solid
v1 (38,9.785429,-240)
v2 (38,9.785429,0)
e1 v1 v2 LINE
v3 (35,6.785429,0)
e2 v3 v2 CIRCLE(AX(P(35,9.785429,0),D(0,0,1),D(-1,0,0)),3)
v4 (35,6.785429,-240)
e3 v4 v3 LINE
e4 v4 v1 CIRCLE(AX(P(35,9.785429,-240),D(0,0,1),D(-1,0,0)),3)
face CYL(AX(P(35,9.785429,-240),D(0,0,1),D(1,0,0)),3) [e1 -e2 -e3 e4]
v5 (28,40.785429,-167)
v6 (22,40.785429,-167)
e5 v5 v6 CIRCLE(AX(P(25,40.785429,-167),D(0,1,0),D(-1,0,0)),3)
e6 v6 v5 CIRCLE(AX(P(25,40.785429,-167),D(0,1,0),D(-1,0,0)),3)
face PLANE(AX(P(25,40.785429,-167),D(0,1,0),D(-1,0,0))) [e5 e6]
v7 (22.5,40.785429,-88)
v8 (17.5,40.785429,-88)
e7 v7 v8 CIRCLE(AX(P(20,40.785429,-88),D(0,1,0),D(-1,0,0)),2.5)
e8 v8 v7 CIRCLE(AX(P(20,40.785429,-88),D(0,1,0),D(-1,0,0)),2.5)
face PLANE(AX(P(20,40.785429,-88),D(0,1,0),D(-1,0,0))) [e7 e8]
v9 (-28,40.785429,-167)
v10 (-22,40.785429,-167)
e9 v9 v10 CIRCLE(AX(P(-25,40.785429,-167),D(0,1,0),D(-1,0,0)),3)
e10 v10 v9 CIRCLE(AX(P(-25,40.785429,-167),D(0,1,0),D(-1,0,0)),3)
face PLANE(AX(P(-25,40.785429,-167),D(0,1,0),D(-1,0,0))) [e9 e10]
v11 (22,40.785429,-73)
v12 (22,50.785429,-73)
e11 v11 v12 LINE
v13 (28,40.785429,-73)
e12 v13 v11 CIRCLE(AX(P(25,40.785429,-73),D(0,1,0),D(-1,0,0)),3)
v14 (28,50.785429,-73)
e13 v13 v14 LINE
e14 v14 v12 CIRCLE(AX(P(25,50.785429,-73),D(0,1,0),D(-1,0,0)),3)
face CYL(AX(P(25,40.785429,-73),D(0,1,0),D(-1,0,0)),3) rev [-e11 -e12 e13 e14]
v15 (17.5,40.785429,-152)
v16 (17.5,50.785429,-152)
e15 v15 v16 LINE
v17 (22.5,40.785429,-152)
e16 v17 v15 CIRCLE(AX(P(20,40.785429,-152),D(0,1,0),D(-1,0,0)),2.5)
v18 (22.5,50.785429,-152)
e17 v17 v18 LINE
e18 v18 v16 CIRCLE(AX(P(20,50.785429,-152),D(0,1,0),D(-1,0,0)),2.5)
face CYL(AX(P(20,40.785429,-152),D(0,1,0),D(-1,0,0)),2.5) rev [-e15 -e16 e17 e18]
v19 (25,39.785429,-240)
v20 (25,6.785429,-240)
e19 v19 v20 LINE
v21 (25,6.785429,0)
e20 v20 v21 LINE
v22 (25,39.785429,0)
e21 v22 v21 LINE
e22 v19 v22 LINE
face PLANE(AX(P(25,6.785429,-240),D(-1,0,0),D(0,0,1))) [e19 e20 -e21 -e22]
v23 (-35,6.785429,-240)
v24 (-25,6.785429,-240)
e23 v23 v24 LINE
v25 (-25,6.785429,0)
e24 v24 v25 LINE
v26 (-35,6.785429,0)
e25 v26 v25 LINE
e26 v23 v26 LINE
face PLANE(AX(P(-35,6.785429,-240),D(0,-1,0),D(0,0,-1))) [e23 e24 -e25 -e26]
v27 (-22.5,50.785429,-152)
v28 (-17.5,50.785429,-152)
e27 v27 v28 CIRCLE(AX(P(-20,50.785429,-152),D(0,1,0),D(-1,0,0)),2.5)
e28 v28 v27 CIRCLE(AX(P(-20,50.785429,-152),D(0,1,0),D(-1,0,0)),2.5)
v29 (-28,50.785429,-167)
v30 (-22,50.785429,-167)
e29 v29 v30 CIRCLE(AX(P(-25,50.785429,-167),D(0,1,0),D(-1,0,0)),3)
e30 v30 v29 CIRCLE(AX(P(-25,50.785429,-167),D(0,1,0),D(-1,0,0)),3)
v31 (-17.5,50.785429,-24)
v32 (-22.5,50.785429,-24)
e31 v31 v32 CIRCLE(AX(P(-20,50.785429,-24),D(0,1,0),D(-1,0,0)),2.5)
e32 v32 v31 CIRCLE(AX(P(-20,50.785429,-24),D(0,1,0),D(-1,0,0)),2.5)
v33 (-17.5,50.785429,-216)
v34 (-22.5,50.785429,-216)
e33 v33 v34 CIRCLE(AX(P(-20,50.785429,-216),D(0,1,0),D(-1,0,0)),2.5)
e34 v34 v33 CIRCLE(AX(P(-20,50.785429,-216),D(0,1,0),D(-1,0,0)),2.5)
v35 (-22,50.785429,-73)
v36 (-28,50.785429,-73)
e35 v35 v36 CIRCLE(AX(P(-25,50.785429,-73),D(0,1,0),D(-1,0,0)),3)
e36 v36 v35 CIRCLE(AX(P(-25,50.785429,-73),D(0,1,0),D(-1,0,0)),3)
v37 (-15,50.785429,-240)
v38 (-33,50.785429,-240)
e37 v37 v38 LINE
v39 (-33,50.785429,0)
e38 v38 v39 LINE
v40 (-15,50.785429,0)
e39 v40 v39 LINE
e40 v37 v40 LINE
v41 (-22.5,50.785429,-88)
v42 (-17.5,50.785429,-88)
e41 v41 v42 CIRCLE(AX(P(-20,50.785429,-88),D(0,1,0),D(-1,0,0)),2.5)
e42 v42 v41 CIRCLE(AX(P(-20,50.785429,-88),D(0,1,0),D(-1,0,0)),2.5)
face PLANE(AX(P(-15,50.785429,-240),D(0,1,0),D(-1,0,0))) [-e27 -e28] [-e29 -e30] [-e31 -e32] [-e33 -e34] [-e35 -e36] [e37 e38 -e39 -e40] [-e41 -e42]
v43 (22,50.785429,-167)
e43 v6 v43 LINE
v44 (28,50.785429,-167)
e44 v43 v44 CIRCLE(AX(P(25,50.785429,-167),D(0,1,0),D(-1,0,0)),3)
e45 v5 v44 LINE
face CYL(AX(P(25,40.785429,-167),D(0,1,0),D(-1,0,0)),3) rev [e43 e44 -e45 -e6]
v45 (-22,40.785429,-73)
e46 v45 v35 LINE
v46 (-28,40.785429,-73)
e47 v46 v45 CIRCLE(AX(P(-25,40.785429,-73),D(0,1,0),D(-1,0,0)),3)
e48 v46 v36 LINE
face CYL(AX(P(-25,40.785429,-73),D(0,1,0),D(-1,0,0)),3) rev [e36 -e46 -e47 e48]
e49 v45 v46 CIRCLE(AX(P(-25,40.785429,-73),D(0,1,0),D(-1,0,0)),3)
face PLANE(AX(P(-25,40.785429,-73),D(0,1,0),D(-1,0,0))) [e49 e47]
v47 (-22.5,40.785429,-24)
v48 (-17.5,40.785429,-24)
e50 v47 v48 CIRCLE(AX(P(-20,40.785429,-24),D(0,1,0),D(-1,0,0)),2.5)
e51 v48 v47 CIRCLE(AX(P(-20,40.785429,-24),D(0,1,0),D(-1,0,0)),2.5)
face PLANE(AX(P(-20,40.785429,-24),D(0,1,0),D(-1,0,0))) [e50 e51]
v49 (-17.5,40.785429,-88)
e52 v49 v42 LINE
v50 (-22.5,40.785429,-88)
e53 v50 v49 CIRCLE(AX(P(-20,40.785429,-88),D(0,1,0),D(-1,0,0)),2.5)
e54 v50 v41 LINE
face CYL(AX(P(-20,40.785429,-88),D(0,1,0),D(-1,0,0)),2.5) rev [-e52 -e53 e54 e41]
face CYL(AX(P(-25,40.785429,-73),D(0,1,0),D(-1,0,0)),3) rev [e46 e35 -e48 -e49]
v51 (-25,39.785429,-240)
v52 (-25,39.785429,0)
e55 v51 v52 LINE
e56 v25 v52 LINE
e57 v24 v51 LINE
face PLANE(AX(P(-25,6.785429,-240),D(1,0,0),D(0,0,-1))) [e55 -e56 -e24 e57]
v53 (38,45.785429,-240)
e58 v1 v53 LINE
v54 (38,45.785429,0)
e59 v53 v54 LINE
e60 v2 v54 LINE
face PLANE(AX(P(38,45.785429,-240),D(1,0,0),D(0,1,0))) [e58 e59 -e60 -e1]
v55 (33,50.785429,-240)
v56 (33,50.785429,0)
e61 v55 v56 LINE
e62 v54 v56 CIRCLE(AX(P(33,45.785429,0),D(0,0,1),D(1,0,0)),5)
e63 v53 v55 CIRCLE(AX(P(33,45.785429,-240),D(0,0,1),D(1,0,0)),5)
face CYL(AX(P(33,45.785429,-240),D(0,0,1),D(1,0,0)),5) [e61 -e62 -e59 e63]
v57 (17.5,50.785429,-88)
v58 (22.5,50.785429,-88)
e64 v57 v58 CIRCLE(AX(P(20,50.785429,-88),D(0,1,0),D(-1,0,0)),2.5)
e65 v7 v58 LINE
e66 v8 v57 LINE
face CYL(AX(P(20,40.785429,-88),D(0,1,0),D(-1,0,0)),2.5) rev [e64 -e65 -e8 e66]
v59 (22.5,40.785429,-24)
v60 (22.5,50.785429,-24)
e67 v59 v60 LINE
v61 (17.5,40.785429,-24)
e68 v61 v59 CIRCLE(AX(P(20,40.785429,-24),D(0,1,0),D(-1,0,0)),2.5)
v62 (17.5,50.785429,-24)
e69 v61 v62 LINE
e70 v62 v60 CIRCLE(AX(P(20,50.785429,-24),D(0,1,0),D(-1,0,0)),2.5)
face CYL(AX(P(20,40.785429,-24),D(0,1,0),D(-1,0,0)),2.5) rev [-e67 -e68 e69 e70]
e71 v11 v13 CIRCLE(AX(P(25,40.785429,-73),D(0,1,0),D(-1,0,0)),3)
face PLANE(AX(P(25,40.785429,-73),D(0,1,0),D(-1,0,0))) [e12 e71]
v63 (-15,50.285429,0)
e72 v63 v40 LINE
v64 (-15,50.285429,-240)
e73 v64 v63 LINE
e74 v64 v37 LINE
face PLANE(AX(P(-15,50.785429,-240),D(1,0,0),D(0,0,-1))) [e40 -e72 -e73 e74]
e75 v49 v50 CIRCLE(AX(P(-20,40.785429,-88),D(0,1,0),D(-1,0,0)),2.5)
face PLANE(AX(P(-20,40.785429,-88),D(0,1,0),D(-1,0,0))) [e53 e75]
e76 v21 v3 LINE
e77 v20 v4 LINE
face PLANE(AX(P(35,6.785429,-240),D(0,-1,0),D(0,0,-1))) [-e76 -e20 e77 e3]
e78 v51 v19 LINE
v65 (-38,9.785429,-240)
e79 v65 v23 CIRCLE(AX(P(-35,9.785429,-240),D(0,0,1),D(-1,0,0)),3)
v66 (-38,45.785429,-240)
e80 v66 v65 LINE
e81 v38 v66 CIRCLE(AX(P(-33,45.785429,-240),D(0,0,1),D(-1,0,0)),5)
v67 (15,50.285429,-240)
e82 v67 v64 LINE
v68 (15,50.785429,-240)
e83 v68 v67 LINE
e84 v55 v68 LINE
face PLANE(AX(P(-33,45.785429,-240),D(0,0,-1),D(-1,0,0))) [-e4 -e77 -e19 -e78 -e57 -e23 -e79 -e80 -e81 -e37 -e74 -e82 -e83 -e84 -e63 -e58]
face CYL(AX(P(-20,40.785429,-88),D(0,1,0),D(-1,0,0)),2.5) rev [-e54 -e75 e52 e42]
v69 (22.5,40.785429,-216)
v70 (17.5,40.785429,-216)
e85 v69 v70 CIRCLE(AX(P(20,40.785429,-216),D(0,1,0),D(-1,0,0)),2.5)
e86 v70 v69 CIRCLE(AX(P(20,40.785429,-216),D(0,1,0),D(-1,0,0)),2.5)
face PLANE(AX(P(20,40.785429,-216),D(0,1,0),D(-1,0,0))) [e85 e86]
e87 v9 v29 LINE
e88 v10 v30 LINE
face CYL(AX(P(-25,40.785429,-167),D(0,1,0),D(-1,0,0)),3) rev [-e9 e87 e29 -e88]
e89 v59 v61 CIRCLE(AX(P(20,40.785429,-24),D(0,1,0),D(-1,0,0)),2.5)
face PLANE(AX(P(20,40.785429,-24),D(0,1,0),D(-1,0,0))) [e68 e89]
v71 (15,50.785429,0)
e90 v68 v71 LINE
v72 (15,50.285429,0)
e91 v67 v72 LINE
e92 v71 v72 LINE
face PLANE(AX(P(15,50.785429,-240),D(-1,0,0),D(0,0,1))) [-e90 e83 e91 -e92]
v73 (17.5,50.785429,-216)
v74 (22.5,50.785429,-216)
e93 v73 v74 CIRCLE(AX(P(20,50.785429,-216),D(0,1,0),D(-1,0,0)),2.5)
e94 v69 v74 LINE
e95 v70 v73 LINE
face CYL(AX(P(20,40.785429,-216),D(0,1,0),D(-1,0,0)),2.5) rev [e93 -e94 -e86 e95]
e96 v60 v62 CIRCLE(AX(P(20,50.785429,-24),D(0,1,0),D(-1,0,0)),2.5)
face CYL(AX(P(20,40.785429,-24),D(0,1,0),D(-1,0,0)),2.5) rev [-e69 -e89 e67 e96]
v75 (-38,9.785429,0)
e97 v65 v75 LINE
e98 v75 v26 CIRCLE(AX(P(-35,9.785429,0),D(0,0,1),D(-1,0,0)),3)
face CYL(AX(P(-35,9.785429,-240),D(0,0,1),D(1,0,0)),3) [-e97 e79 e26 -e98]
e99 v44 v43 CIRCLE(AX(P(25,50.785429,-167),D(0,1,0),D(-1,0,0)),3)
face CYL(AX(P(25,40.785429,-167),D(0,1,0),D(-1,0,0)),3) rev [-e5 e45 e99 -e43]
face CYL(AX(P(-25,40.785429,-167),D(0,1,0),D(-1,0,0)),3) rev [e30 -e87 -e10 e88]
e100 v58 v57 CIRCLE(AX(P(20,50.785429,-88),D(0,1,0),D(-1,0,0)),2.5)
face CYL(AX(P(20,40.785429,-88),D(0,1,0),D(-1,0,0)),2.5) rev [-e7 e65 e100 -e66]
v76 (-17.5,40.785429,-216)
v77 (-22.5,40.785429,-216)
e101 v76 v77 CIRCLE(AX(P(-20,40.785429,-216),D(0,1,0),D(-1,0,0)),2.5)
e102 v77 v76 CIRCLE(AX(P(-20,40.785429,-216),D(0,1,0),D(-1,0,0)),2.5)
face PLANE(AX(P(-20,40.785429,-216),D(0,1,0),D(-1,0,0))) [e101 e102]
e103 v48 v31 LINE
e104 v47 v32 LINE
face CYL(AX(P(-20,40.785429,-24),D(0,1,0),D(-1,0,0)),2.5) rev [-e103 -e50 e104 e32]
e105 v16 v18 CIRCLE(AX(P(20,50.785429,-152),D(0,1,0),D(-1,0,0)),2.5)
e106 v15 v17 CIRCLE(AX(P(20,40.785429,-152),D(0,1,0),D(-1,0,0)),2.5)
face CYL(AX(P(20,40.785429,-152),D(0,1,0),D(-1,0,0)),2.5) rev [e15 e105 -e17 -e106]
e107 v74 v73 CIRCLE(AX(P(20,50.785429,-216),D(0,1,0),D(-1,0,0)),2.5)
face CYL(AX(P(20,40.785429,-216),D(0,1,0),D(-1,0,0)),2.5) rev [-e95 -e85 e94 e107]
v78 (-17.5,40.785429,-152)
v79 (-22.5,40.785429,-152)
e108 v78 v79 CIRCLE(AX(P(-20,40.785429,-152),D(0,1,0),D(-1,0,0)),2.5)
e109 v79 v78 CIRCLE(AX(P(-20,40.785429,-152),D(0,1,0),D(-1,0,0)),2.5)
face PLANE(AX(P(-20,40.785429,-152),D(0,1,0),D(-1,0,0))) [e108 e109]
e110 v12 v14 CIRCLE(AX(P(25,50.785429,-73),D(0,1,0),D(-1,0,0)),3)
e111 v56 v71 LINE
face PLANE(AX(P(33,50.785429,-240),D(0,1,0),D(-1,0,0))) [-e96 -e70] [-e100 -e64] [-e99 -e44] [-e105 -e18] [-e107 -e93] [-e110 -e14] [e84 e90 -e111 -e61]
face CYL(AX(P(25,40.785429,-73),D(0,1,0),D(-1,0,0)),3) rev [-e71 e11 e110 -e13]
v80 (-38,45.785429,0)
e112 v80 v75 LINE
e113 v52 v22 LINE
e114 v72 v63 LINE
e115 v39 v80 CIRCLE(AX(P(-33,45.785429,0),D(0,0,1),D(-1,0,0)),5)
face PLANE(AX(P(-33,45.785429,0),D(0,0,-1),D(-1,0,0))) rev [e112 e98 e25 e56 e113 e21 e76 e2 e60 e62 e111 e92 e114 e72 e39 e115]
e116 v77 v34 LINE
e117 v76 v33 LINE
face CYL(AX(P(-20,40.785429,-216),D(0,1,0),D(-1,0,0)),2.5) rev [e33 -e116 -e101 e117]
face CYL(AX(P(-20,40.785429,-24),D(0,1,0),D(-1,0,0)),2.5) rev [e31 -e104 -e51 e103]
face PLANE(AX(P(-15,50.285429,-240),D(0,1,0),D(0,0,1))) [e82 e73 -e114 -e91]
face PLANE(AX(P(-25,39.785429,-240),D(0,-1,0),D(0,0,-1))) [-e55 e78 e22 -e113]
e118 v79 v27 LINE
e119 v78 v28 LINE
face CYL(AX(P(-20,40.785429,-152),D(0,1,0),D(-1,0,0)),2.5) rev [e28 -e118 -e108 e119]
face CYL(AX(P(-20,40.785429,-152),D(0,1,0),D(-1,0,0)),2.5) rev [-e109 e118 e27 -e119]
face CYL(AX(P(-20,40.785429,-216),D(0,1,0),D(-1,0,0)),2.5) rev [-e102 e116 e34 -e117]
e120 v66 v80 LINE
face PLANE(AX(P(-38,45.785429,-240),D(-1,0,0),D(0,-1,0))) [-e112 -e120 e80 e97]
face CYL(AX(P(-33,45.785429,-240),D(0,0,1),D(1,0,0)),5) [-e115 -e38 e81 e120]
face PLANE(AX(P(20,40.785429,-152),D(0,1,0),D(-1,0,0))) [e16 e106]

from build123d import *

# Parameters (mm, degrees)
EXTRUDE_406_DEPTH   = 240
SKETCH_3_R          = 2.5
SKETCH_3_R_2        = 3
CUT_EXTRUDE_1_DEPTH = 10


with BuildPart() as part:
    # 草图1 → Extrude 406 (new body)
    with BuildSketch(Plane.XY):
        with BuildLine():
            Line((33, 50.785428571), (15, 50.785428571))
            Line((15, 50.785428571), (15, 50.285428571))
            Line((15, 50.285428571), (-15, 50.285428571))
            Line((-15, 50.285428571), (-15, 50.785428571))
            Line((-15, 50.785428571), (-33, 50.785428571))
            ThreePointArc((-33, 50.785428571), (-36.535533906, 49.320962477), (-38, 45.785428571))
            Line((-38, 45.785428571), (-38, 9.785428571))
            ThreePointArc((-38, 9.785428571), (-37.121320344, 7.664108228), (-35, 6.785428571))
            Line((-35, 6.785428571), (-25, 6.785428571))
            Line((-25, 6.785428571), (-25, 39.785428571))
            Line((-25, 39.785428571), (25, 39.785428571))
            Line((25, 39.785428571), (25, 6.785428571))
            Line((25, 6.785428571), (35, 6.785428571))
            ThreePointArc((35, 6.785428571), (37.121320344, 7.664108228), (38, 9.785428571))
            Line((38, 9.785428571), (38, 45.785428571))
            ThreePointArc((38, 45.785428571), (36.535533906, 49.320962477), (33, 50.785428571))
        make_face()
    extrude(amount=-EXTRUDE_406_DEPTH)

    # 草图3 → 切除-拉伸1 (cut)
    with BuildSketch(Plane(origin=(0, 50.785428571, 0), x_dir=(-1, 0, 0), z_dir=(0, 1, 0))):
        with Locations((-20, -24)):
            Circle(SKETCH_3_R)
        with Locations((20, -24)):
            Circle(SKETCH_3_R)
        with Locations((-20, -88)):
            Circle(SKETCH_3_R)
        with Locations((20, -88)):
            Circle(SKETCH_3_R)
        with Locations((-20, -152)):
            Circle(SKETCH_3_R)
        with Locations((20, -152)):
            Circle(SKETCH_3_R)
        with Locations((-20, -216)):
            Circle(SKETCH_3_R)
        with Locations((20, -216)):
            Circle(SKETCH_3_R)
        with Locations((-25, -73)):
            Circle(SKETCH_3_R_2)
        with Locations((25, -73)):
            Circle(SKETCH_3_R_2)
        with Locations((-25, -167)):
            Circle(SKETCH_3_R_2)
        with Locations((25, -167)):
            Circle(SKETCH_3_R_2)
    extrude(amount=-CUT_EXTRUDE_1_DEPTH, mode=Mode.SUBTRACT)


solid = part.part
